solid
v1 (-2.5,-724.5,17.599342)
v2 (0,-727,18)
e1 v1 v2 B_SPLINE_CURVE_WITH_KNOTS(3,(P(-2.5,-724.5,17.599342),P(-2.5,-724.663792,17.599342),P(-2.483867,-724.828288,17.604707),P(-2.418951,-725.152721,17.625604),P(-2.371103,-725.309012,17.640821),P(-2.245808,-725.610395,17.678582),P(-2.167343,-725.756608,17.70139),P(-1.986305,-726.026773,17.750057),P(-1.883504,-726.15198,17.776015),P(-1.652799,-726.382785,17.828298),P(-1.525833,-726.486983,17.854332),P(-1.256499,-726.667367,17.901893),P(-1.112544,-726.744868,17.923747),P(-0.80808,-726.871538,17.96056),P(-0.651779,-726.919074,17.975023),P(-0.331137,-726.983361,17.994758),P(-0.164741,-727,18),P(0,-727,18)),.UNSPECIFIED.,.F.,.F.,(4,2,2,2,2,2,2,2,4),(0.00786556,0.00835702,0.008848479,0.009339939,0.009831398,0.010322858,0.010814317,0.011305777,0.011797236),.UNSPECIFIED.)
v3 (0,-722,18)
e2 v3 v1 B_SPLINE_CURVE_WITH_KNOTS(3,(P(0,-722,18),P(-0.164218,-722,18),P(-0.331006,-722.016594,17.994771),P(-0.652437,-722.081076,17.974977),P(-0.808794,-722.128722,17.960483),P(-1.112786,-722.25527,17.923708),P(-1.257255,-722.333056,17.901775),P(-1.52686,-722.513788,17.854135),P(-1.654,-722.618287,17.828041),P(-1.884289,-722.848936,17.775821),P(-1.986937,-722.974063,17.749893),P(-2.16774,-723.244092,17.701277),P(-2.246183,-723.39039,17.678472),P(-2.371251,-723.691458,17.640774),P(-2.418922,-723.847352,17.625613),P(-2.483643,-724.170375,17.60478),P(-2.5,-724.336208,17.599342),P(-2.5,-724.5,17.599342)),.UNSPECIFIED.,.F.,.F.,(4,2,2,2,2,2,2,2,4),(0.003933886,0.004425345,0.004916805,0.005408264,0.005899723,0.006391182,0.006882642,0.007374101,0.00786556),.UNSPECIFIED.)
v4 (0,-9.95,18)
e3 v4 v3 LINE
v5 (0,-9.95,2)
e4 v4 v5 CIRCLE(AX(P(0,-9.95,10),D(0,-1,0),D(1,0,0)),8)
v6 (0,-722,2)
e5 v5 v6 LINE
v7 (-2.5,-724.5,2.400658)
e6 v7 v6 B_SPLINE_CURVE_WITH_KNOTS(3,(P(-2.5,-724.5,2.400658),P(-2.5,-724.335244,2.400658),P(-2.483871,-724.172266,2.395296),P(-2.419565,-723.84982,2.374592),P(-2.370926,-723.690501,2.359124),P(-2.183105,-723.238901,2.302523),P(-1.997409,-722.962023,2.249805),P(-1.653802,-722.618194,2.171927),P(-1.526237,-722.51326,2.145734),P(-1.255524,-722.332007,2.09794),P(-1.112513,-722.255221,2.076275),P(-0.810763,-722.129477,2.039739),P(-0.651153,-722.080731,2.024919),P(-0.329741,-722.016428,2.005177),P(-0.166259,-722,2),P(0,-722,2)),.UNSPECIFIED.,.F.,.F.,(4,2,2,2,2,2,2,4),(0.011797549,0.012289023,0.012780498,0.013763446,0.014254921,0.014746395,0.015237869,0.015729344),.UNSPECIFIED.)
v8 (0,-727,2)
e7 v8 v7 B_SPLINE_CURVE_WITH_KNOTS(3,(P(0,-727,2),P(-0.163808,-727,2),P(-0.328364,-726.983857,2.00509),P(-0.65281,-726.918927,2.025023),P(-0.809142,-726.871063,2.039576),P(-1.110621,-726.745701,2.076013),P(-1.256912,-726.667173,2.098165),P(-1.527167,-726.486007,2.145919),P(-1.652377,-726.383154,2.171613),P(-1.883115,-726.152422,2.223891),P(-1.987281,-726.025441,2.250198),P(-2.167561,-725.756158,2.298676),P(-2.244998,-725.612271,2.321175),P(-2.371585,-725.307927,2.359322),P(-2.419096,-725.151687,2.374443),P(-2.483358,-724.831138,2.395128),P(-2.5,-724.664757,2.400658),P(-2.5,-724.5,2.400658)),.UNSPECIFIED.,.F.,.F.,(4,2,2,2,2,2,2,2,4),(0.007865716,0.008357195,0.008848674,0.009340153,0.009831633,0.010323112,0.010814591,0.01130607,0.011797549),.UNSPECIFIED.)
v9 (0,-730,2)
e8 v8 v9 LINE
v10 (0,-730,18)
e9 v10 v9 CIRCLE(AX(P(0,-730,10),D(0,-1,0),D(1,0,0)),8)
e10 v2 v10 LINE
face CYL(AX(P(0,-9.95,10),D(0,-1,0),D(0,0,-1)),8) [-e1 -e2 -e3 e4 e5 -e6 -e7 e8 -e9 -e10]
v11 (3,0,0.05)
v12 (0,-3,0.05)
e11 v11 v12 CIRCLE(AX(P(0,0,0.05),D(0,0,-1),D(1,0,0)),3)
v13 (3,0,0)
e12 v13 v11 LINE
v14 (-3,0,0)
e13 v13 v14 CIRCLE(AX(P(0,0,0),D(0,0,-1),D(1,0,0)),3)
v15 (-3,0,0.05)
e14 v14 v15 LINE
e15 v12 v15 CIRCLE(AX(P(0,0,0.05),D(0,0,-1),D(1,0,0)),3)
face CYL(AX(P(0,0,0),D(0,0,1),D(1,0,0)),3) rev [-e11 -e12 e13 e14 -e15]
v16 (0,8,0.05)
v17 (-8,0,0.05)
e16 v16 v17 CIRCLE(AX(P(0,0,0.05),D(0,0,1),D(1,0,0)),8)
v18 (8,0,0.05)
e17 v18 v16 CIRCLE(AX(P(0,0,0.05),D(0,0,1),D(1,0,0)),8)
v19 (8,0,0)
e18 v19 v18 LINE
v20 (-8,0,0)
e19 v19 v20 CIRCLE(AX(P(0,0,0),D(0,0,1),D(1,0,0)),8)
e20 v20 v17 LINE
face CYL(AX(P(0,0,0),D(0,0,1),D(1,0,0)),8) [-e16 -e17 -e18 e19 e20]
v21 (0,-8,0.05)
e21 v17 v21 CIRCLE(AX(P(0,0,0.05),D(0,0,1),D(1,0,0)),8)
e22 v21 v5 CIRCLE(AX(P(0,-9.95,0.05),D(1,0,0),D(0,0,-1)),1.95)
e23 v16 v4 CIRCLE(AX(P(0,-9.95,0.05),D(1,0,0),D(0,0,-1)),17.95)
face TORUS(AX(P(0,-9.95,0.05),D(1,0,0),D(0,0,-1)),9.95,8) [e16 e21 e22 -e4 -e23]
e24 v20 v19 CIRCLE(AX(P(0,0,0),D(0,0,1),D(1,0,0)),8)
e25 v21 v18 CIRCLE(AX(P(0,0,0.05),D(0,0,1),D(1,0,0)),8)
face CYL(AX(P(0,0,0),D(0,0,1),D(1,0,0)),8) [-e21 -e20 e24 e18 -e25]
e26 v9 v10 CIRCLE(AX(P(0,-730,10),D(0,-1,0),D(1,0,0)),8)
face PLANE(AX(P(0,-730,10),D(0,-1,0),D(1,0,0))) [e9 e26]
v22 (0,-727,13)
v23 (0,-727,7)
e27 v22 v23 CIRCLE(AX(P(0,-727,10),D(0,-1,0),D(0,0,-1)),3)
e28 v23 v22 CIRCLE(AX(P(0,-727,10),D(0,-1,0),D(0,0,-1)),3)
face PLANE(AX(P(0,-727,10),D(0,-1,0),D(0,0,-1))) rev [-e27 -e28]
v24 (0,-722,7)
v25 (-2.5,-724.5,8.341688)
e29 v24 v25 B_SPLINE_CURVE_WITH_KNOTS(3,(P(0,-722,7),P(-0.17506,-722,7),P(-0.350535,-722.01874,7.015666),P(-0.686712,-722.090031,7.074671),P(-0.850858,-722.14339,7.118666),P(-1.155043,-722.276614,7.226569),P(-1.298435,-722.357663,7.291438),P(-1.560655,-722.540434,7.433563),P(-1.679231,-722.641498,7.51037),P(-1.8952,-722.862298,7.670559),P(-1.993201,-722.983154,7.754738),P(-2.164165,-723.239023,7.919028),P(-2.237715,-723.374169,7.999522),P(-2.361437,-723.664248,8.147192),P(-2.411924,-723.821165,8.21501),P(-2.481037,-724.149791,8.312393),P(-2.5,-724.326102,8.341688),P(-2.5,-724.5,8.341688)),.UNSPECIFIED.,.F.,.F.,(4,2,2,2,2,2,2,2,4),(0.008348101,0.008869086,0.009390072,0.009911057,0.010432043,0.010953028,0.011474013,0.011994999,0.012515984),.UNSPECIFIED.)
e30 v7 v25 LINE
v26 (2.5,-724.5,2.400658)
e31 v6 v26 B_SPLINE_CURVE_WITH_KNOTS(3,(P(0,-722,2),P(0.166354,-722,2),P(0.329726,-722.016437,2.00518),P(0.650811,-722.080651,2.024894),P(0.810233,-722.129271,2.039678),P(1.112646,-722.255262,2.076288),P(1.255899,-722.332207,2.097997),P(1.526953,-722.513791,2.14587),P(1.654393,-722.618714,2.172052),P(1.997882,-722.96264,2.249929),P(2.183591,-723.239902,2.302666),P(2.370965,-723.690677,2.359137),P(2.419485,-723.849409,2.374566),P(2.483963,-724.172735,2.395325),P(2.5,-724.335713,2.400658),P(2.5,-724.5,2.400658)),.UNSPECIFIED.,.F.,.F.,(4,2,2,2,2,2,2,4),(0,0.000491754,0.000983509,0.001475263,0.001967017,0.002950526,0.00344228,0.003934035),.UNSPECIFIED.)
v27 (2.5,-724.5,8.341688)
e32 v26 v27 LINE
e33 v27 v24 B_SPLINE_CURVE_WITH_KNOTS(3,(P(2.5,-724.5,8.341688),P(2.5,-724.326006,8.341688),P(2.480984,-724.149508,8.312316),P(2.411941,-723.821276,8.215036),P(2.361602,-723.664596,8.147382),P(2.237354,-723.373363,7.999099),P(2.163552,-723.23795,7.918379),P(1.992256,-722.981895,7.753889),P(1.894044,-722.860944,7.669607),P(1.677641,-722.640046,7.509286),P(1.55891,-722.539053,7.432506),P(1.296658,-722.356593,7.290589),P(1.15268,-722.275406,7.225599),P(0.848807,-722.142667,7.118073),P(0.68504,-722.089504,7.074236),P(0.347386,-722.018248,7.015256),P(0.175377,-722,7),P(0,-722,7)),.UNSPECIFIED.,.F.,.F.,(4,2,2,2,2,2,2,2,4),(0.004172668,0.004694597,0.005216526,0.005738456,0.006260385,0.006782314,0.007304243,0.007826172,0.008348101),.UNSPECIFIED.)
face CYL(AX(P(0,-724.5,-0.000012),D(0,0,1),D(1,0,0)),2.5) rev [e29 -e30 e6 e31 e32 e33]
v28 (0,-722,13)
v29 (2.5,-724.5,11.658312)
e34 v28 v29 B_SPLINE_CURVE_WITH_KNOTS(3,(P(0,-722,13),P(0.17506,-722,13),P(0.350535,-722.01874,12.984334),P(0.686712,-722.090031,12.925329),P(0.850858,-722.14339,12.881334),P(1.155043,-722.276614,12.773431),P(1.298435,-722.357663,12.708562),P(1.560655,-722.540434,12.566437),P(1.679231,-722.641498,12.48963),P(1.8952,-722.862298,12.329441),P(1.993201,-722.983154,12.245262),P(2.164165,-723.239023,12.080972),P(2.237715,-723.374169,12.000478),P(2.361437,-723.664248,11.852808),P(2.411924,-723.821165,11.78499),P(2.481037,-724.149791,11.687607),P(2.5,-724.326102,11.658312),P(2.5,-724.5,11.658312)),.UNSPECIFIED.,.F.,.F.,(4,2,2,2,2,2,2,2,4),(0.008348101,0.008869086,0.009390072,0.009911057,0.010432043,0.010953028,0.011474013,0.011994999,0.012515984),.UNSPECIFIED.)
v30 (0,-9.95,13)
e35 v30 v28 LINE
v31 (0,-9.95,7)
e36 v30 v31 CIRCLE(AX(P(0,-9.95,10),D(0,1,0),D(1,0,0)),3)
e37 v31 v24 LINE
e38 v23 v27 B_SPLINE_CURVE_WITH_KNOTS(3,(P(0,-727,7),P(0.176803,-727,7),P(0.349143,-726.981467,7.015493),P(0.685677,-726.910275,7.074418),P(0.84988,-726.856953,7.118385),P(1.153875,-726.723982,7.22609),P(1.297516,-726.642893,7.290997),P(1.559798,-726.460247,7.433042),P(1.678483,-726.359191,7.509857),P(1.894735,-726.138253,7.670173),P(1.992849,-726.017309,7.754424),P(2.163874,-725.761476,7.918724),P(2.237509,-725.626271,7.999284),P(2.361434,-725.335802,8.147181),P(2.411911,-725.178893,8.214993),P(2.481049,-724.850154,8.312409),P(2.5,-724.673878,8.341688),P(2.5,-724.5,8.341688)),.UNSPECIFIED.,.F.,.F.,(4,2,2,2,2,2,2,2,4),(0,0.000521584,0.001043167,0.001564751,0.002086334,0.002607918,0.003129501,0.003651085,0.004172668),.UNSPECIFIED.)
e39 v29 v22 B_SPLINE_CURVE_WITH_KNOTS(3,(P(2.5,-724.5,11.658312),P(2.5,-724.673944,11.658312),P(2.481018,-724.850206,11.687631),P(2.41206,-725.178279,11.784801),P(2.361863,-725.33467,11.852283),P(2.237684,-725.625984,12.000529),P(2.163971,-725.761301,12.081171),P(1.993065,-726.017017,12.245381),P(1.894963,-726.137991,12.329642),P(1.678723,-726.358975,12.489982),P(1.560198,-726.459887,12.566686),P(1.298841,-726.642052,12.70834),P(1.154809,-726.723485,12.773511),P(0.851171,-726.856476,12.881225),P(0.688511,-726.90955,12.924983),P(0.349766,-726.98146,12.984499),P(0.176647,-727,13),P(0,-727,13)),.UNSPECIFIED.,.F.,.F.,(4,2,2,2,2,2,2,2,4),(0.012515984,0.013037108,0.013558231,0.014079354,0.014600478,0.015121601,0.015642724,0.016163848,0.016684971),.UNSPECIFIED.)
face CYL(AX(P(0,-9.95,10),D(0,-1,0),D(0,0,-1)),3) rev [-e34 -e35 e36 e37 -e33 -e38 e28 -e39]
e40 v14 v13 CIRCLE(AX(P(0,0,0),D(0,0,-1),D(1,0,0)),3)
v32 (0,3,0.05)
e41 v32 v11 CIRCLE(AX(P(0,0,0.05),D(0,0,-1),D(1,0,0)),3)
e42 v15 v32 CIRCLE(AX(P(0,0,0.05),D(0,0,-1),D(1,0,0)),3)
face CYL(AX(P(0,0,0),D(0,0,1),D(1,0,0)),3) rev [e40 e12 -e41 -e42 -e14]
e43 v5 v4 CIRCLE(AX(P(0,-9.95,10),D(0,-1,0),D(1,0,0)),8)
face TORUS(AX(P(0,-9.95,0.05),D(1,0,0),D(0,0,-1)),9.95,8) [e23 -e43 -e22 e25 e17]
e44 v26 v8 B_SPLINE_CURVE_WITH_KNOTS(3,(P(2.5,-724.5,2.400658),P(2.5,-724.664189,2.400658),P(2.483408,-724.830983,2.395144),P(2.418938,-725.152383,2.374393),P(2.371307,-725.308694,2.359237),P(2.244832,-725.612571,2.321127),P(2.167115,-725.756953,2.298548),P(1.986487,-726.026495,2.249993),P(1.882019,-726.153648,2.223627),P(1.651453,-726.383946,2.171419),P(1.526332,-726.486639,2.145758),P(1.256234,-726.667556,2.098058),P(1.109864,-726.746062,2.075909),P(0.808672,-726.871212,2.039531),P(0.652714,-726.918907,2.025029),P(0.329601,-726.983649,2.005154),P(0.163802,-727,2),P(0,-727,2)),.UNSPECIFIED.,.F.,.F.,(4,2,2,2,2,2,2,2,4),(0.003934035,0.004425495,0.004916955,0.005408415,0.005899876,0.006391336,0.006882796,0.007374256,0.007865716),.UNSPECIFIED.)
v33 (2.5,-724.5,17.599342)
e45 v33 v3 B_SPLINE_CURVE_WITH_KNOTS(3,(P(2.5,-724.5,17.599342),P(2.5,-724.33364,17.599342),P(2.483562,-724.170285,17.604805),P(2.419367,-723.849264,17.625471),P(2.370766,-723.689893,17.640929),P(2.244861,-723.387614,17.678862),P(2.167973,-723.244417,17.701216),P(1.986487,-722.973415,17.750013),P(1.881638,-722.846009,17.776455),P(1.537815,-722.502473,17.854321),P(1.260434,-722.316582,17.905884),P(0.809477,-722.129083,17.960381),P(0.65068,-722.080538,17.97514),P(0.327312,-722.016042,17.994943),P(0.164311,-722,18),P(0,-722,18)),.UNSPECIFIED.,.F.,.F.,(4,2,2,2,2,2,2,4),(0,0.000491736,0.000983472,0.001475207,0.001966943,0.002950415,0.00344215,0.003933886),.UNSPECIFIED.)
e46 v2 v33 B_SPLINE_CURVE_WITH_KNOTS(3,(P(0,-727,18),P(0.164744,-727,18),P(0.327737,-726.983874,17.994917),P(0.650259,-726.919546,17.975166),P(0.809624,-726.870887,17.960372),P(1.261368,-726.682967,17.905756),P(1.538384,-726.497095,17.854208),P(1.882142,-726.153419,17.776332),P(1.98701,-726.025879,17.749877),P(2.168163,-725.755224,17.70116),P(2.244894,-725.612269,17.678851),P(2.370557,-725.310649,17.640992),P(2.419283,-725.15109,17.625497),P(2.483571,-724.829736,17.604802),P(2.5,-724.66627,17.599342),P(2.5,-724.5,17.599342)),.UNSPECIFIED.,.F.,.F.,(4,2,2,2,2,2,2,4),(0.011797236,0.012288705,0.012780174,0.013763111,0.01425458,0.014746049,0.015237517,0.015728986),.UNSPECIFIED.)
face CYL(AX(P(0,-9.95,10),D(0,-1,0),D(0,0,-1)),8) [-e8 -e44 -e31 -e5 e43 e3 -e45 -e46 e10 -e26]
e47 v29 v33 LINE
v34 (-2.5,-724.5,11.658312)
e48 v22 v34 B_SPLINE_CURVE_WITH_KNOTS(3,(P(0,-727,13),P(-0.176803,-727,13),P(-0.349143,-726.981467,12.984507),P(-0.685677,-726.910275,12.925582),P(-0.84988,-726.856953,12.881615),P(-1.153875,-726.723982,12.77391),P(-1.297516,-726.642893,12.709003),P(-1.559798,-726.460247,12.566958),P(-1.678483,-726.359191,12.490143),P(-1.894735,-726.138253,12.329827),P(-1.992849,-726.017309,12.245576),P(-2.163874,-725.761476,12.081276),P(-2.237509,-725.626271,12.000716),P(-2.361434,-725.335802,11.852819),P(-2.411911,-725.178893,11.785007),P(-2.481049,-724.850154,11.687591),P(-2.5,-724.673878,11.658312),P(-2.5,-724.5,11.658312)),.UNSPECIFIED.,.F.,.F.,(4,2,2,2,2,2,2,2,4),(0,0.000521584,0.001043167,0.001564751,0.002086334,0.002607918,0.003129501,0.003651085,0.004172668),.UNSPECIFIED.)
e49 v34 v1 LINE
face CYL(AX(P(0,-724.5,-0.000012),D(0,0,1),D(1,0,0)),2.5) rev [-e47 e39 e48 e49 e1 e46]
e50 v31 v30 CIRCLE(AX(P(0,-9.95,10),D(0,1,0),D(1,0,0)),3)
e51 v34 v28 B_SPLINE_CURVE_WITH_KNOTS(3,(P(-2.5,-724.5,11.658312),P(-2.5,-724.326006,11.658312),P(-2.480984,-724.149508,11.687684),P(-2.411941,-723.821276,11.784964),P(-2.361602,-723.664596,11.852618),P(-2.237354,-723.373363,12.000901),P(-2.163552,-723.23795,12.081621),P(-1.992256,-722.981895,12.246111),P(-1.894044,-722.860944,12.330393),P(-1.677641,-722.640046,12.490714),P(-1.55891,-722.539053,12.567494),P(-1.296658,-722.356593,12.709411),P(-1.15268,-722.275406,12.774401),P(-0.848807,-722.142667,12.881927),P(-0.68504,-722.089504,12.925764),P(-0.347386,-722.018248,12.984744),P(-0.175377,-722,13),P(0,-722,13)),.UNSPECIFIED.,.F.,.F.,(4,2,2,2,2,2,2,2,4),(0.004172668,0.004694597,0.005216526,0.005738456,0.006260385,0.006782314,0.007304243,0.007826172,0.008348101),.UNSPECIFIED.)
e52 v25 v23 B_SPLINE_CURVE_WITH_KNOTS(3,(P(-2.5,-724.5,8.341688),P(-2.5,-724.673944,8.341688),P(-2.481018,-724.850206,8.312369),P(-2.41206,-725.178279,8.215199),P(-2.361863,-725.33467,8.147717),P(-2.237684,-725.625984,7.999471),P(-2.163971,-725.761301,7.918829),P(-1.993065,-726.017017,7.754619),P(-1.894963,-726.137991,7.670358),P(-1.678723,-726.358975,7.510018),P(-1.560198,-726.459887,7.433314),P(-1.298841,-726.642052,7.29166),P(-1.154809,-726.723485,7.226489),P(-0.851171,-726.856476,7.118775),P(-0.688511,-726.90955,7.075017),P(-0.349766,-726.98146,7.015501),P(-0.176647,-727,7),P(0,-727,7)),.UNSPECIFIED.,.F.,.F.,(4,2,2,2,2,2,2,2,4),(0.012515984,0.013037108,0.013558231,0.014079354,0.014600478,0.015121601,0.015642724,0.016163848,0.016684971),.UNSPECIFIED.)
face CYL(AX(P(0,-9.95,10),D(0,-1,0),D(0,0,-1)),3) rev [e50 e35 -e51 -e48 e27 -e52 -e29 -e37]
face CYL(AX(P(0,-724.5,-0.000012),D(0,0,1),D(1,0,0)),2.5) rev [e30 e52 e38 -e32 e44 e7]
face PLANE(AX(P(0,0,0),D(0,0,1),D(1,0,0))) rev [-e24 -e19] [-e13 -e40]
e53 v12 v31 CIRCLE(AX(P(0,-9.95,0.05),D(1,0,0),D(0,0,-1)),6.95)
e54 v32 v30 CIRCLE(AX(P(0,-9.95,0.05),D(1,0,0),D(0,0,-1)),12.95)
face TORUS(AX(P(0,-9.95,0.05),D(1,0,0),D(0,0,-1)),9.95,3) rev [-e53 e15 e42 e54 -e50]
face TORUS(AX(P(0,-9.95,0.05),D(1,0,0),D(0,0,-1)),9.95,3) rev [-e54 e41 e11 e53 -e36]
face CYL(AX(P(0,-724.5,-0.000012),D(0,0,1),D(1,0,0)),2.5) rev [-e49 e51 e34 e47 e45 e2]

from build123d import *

# Parameters (mm, degrees)
SKETCH1_R               = 8
SKETCH1_R_2             = 3
SKETCH3_R               = 3
BOSS_EXTRUDE1_DEPTH     = 3
CUT_EXTRUDE2_DEPTH      = 731.265705073
CUT_EXTRUDE2_DEPTH_BACK = 731.265705073
SKETCH4_R               = 2.5


with BuildPart() as part:
    # Sweep1: sweep along a path in Sketch2
    with BuildLine(Plane(origin=(0, 0, 0), x_dir=(0, 0, -1), z_dir=(1, 0, 0))) as sweep1_path:
        Line((0, 0), (-0.05, 0))
        ThreePointArc((-0.05, 0), (-7.085712473, -2.914287527), (-10, -9.95))
        Line((-10, -9.95), (-10, -730))
    # Sketch1 → Sweep1 (sweep)
    with BuildSketch(Plane.XY):
        Circle(SKETCH1_R)
        Circle(SKETCH1_R_2, mode=Mode.SUBTRACT)
    sweep(path=sweep1_path.line)

    # Sketch3 → Boss-Extrude1 (add)
    with BuildSketch(Plane.XZ.offset(730)):
        with Locations(Location((0, 10, 0), (0, 0, 270))):
            Circle(SKETCH3_R)
    extrude(amount=-BOSS_EXTRUDE1_DEPTH)

    # Sketch4 → Cut-Extrude2 (cut, two sides: drawn at the far end of the back side and taken through both)
    with BuildSketch(Plane.XY.offset(-CUT_EXTRUDE2_DEPTH_BACK)):
        with Locations((0, -724.5)):
            Circle(SKETCH4_R)
    extrude(amount=CUT_EXTRUDE2_DEPTH + CUT_EXTRUDE2_DEPTH_BACK, mode=Mode.SUBTRACT)


solid = part.part
